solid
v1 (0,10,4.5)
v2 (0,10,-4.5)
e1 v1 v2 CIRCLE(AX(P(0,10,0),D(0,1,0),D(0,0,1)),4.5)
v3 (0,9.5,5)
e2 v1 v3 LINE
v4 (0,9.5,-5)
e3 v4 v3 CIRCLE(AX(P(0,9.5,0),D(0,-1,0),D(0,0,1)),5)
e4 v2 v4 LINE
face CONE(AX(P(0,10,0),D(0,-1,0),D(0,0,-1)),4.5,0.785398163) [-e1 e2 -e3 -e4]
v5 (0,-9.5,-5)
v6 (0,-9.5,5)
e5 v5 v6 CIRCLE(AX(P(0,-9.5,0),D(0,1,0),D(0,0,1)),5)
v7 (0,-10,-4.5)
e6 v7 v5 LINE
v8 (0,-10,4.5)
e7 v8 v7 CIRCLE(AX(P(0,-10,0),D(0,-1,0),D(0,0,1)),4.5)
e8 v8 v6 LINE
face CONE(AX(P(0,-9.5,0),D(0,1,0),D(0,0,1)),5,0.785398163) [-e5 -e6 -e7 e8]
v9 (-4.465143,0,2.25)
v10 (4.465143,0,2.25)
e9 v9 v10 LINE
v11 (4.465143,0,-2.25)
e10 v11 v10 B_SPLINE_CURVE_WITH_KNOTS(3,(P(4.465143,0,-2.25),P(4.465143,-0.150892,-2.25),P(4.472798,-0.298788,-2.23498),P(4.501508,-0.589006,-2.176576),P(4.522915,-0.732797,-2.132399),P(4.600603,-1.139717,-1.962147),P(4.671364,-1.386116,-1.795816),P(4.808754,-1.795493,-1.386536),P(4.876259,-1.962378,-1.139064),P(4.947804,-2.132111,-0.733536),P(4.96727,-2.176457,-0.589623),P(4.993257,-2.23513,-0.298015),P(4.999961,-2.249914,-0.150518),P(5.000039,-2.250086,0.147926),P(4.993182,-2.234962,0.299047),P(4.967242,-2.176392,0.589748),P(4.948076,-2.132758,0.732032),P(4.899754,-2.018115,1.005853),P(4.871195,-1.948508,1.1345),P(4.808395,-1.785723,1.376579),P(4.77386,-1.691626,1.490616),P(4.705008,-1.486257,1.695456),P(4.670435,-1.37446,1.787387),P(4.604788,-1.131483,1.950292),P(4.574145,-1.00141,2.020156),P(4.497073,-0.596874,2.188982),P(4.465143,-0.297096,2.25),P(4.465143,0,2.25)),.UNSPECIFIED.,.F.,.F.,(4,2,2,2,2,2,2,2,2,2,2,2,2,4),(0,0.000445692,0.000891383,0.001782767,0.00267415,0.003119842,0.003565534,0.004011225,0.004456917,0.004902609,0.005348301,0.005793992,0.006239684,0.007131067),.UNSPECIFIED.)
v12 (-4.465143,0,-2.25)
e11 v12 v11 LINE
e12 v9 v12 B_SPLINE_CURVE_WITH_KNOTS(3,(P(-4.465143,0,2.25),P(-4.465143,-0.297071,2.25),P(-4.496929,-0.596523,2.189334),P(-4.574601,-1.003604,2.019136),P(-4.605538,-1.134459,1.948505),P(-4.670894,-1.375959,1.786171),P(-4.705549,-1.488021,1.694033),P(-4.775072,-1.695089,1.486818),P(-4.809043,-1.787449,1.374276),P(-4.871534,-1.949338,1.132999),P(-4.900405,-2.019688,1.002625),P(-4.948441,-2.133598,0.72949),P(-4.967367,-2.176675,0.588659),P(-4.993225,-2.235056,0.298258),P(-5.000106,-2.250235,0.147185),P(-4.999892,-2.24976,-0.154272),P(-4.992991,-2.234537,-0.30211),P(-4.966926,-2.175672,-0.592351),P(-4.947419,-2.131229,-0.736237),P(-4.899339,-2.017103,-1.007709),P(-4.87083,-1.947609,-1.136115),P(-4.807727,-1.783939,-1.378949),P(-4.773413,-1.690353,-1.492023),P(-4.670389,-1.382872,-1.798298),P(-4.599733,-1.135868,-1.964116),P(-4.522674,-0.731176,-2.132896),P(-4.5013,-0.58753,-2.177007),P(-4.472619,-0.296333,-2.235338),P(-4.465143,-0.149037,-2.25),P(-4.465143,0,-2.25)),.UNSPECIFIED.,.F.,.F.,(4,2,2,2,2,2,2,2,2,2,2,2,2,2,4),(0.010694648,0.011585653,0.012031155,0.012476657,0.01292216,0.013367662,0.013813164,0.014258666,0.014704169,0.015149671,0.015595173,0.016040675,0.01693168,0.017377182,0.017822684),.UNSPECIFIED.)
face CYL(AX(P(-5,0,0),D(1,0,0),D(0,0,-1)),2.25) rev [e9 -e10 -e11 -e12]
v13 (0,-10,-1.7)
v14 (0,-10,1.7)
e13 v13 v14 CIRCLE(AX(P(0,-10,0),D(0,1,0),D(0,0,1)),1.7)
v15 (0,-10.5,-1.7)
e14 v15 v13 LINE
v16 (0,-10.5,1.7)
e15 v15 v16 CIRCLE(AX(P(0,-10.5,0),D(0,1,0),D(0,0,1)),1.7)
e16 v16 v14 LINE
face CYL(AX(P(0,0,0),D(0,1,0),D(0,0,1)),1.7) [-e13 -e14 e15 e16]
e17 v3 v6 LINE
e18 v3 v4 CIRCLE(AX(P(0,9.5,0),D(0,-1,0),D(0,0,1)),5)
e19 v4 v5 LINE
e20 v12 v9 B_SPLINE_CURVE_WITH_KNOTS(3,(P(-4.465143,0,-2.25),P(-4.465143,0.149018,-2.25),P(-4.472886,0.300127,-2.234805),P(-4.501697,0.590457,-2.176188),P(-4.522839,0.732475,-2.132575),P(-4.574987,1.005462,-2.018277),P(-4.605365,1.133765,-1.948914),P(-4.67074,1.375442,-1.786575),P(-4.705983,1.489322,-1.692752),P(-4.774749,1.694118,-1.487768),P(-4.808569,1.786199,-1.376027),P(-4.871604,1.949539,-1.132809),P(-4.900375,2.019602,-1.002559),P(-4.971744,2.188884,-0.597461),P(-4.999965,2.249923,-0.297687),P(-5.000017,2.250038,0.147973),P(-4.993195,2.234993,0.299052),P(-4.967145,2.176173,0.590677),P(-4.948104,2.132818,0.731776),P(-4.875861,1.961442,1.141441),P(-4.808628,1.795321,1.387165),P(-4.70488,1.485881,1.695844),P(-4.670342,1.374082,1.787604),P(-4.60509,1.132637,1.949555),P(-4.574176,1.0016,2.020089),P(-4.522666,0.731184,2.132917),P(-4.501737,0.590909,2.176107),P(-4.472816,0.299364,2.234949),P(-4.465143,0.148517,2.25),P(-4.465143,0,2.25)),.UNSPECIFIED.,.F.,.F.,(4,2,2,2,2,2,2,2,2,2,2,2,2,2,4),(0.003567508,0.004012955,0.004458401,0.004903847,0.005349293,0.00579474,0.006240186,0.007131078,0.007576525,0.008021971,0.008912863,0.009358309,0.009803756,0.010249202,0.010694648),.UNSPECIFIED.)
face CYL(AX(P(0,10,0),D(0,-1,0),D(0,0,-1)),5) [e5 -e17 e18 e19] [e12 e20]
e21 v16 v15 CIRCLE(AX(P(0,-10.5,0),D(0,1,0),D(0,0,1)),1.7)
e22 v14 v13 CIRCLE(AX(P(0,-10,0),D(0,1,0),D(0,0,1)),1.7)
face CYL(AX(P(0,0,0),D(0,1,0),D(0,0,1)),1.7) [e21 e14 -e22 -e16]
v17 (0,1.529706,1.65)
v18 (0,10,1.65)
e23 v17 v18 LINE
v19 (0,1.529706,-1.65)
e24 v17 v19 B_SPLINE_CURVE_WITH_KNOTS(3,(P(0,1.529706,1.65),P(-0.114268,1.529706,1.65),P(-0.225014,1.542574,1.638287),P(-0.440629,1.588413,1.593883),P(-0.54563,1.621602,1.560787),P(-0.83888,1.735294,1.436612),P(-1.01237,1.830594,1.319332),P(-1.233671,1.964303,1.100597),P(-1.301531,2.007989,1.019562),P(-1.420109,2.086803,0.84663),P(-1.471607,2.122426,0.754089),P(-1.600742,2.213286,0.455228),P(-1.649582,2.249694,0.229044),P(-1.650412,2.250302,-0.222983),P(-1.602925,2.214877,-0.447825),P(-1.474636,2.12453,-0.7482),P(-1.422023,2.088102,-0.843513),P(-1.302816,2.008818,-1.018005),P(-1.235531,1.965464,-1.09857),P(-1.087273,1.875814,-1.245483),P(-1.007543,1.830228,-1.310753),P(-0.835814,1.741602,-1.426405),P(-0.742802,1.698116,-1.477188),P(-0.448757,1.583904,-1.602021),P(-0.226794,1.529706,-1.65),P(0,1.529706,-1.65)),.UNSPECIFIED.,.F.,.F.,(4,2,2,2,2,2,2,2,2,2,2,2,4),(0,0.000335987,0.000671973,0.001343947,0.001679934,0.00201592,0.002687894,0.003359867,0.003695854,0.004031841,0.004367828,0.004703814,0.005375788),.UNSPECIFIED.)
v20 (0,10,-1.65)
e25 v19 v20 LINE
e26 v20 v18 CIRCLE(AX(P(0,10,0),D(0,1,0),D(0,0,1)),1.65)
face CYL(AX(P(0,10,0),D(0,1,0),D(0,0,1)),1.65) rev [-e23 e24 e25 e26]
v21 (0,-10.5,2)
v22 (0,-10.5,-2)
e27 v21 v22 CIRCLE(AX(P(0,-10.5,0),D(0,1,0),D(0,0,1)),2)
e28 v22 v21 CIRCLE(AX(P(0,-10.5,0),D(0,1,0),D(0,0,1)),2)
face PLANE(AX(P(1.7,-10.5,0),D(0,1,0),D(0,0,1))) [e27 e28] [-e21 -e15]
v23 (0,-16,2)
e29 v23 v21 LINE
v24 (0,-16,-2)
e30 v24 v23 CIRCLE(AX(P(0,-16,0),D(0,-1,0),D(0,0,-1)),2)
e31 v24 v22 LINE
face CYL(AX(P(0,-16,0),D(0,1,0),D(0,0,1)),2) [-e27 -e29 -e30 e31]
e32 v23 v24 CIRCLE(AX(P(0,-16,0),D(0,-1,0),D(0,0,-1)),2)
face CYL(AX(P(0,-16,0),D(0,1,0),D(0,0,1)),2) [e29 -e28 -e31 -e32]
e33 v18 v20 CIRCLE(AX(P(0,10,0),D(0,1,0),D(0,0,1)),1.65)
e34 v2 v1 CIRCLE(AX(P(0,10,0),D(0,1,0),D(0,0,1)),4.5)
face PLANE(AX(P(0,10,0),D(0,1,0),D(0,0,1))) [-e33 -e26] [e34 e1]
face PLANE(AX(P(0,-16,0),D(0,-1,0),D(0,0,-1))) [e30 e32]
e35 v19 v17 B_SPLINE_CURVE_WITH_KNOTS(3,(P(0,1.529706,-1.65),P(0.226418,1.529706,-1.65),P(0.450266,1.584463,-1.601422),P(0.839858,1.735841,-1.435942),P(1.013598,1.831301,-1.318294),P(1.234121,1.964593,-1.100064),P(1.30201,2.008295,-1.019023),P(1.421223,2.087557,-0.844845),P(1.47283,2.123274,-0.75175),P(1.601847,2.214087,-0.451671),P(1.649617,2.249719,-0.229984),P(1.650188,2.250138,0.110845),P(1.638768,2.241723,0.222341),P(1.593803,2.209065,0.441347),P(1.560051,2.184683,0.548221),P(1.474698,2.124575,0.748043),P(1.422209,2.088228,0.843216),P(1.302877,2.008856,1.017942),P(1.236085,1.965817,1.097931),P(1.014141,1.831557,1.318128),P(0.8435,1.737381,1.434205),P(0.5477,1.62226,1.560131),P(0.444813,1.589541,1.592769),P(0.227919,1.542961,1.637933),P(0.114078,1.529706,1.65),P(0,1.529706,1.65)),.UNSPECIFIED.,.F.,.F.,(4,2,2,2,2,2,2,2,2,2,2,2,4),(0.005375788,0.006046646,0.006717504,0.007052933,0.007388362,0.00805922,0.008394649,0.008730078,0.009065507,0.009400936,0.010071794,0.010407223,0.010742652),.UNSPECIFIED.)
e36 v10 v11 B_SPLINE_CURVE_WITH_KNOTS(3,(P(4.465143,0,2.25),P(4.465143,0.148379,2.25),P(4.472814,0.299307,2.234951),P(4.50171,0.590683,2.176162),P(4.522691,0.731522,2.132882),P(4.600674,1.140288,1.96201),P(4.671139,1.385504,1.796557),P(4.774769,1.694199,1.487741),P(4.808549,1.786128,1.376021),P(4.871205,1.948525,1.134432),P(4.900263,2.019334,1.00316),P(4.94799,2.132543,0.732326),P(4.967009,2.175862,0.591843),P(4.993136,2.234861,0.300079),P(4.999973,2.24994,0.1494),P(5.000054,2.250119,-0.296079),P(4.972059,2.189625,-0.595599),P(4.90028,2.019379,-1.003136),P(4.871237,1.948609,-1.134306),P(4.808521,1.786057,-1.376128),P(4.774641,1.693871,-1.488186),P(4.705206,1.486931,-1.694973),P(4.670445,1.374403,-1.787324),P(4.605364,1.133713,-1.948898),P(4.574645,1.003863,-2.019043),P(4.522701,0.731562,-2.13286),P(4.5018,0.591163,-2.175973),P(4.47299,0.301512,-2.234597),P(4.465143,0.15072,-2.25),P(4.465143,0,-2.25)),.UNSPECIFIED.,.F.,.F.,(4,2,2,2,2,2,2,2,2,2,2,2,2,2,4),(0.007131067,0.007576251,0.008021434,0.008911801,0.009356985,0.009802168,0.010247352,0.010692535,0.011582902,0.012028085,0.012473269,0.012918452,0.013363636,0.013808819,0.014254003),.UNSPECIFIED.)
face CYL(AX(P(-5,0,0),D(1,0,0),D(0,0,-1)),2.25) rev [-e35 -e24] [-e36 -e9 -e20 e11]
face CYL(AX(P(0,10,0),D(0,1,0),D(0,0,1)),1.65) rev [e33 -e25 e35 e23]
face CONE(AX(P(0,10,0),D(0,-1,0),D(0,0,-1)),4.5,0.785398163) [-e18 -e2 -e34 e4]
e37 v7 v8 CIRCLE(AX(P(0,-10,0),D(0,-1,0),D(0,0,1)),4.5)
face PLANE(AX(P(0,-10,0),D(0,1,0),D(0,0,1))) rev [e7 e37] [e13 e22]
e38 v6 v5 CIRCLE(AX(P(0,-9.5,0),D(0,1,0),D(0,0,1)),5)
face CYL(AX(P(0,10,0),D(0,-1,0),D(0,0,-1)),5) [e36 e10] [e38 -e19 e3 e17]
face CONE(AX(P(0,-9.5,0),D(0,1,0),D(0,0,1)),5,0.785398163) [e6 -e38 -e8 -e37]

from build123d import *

# Parameters (mm, degrees)
SKETCH_1_R               = 5
EXTRUDE_1_DEPTH          = 10
SKETCH_2_R               = 2
EXTRUDE_2_DEPTH          = 6
SKETCH_3_W               = 0.3
SKETCH_3_H               = 0.5
HOLE_WIZARD_M4_1_D       = 3.3
HOLE_WIZARD_M4_1_DEPTH   = 10.1
HOLE_WIZARD_M4_1_TIP     = 0.991420021
CHAMFER_1_SIZE           = 0.5
CUT_EXTRUDE_1_DEPTH      = 18.492855685
CUT_EXTRUDE_1_DEPTH_BACK = 18.492855685
SKETCH_6_R               = 2.25


with BuildPart() as part:
    # 草图1 → 凸台-拉伸1 (new, symmetric)
    with BuildSketch(Plane(origin=(0, 0, 0), x_dir=(1, 0, 0), z_dir=(0, 1, 0))):
        with Locations(Location((0, 0, 0), (0, 0, 270))):
            Circle(SKETCH_1_R)
    extrude(amount=EXTRUDE_1_DEPTH, both=True)

    # 草图2 → 凸台-拉伸2 (add)
    with BuildSketch(Plane.XZ.offset(10)):
        with Locations(Location((0, 0, 0), (0, 0, 90))):
            Circle(SKETCH_2_R)
    extrude(amount=EXTRUDE_2_DEPTH)

    # 草图3 → 切除-旋转1 (revolve, cut)
    with BuildSketch(Plane.XY, mode=Mode.PRIVATE) as cut_revolve_1_sk:
        with Locations((1.85, -10.25)):
            Rectangle(SKETCH_3_W, SKETCH_3_H)
    revolve(cut_revolve_1_sk.sketch.rotate(Axis((0, 0, 0), (0, -1, 0)), 90), axis=Axis((0, 0, 0), (0, -1, 0)), mode=Mode.SUBTRACT)

    # M4 螺纹孔1
    with Locations(Plane(origin=(0, 10, 0), x_dir=(1, 0, 0), z_dir=(0, 1, 0))):
        with Locations((0, 0)):
            Hole(HOLE_WIZARD_M4_1_D / 2, depth=HOLE_WIZARD_M4_1_DEPTH)
            with Locations((0, 0, -(HOLE_WIZARD_M4_1_DEPTH + HOLE_WIZARD_M4_1_TIP / 2))):  # 118° drill point
                Cone(0, HOLE_WIZARD_M4_1_D / 2, HOLE_WIZARD_M4_1_TIP, mode=Mode.SUBTRACT)

    # 倒角1
    chamfer_1_edges = [part.edges().sort_by_distance(p)[0] for p in [
        (0, -10, -5),
        (0, 10, -5),
    ]]
    chamfer(chamfer_1_edges, length=CHAMFER_1_SIZE)

    # 草图6 → 切除-拉伸1 (cut, two sides: drawn at the far end of the back side and taken through both)
    with BuildSketch(Plane(origin=(0, 0, 0), x_dir=(0, 0, -1), z_dir=(1, 0, 0)).offset(-CUT_EXTRUDE_1_DEPTH_BACK)):
        Circle(SKETCH_6_R)
    extrude(amount=CUT_EXTRUDE_1_DEPTH + CUT_EXTRUDE_1_DEPTH_BACK, mode=Mode.SUBTRACT)


solid = part.part
